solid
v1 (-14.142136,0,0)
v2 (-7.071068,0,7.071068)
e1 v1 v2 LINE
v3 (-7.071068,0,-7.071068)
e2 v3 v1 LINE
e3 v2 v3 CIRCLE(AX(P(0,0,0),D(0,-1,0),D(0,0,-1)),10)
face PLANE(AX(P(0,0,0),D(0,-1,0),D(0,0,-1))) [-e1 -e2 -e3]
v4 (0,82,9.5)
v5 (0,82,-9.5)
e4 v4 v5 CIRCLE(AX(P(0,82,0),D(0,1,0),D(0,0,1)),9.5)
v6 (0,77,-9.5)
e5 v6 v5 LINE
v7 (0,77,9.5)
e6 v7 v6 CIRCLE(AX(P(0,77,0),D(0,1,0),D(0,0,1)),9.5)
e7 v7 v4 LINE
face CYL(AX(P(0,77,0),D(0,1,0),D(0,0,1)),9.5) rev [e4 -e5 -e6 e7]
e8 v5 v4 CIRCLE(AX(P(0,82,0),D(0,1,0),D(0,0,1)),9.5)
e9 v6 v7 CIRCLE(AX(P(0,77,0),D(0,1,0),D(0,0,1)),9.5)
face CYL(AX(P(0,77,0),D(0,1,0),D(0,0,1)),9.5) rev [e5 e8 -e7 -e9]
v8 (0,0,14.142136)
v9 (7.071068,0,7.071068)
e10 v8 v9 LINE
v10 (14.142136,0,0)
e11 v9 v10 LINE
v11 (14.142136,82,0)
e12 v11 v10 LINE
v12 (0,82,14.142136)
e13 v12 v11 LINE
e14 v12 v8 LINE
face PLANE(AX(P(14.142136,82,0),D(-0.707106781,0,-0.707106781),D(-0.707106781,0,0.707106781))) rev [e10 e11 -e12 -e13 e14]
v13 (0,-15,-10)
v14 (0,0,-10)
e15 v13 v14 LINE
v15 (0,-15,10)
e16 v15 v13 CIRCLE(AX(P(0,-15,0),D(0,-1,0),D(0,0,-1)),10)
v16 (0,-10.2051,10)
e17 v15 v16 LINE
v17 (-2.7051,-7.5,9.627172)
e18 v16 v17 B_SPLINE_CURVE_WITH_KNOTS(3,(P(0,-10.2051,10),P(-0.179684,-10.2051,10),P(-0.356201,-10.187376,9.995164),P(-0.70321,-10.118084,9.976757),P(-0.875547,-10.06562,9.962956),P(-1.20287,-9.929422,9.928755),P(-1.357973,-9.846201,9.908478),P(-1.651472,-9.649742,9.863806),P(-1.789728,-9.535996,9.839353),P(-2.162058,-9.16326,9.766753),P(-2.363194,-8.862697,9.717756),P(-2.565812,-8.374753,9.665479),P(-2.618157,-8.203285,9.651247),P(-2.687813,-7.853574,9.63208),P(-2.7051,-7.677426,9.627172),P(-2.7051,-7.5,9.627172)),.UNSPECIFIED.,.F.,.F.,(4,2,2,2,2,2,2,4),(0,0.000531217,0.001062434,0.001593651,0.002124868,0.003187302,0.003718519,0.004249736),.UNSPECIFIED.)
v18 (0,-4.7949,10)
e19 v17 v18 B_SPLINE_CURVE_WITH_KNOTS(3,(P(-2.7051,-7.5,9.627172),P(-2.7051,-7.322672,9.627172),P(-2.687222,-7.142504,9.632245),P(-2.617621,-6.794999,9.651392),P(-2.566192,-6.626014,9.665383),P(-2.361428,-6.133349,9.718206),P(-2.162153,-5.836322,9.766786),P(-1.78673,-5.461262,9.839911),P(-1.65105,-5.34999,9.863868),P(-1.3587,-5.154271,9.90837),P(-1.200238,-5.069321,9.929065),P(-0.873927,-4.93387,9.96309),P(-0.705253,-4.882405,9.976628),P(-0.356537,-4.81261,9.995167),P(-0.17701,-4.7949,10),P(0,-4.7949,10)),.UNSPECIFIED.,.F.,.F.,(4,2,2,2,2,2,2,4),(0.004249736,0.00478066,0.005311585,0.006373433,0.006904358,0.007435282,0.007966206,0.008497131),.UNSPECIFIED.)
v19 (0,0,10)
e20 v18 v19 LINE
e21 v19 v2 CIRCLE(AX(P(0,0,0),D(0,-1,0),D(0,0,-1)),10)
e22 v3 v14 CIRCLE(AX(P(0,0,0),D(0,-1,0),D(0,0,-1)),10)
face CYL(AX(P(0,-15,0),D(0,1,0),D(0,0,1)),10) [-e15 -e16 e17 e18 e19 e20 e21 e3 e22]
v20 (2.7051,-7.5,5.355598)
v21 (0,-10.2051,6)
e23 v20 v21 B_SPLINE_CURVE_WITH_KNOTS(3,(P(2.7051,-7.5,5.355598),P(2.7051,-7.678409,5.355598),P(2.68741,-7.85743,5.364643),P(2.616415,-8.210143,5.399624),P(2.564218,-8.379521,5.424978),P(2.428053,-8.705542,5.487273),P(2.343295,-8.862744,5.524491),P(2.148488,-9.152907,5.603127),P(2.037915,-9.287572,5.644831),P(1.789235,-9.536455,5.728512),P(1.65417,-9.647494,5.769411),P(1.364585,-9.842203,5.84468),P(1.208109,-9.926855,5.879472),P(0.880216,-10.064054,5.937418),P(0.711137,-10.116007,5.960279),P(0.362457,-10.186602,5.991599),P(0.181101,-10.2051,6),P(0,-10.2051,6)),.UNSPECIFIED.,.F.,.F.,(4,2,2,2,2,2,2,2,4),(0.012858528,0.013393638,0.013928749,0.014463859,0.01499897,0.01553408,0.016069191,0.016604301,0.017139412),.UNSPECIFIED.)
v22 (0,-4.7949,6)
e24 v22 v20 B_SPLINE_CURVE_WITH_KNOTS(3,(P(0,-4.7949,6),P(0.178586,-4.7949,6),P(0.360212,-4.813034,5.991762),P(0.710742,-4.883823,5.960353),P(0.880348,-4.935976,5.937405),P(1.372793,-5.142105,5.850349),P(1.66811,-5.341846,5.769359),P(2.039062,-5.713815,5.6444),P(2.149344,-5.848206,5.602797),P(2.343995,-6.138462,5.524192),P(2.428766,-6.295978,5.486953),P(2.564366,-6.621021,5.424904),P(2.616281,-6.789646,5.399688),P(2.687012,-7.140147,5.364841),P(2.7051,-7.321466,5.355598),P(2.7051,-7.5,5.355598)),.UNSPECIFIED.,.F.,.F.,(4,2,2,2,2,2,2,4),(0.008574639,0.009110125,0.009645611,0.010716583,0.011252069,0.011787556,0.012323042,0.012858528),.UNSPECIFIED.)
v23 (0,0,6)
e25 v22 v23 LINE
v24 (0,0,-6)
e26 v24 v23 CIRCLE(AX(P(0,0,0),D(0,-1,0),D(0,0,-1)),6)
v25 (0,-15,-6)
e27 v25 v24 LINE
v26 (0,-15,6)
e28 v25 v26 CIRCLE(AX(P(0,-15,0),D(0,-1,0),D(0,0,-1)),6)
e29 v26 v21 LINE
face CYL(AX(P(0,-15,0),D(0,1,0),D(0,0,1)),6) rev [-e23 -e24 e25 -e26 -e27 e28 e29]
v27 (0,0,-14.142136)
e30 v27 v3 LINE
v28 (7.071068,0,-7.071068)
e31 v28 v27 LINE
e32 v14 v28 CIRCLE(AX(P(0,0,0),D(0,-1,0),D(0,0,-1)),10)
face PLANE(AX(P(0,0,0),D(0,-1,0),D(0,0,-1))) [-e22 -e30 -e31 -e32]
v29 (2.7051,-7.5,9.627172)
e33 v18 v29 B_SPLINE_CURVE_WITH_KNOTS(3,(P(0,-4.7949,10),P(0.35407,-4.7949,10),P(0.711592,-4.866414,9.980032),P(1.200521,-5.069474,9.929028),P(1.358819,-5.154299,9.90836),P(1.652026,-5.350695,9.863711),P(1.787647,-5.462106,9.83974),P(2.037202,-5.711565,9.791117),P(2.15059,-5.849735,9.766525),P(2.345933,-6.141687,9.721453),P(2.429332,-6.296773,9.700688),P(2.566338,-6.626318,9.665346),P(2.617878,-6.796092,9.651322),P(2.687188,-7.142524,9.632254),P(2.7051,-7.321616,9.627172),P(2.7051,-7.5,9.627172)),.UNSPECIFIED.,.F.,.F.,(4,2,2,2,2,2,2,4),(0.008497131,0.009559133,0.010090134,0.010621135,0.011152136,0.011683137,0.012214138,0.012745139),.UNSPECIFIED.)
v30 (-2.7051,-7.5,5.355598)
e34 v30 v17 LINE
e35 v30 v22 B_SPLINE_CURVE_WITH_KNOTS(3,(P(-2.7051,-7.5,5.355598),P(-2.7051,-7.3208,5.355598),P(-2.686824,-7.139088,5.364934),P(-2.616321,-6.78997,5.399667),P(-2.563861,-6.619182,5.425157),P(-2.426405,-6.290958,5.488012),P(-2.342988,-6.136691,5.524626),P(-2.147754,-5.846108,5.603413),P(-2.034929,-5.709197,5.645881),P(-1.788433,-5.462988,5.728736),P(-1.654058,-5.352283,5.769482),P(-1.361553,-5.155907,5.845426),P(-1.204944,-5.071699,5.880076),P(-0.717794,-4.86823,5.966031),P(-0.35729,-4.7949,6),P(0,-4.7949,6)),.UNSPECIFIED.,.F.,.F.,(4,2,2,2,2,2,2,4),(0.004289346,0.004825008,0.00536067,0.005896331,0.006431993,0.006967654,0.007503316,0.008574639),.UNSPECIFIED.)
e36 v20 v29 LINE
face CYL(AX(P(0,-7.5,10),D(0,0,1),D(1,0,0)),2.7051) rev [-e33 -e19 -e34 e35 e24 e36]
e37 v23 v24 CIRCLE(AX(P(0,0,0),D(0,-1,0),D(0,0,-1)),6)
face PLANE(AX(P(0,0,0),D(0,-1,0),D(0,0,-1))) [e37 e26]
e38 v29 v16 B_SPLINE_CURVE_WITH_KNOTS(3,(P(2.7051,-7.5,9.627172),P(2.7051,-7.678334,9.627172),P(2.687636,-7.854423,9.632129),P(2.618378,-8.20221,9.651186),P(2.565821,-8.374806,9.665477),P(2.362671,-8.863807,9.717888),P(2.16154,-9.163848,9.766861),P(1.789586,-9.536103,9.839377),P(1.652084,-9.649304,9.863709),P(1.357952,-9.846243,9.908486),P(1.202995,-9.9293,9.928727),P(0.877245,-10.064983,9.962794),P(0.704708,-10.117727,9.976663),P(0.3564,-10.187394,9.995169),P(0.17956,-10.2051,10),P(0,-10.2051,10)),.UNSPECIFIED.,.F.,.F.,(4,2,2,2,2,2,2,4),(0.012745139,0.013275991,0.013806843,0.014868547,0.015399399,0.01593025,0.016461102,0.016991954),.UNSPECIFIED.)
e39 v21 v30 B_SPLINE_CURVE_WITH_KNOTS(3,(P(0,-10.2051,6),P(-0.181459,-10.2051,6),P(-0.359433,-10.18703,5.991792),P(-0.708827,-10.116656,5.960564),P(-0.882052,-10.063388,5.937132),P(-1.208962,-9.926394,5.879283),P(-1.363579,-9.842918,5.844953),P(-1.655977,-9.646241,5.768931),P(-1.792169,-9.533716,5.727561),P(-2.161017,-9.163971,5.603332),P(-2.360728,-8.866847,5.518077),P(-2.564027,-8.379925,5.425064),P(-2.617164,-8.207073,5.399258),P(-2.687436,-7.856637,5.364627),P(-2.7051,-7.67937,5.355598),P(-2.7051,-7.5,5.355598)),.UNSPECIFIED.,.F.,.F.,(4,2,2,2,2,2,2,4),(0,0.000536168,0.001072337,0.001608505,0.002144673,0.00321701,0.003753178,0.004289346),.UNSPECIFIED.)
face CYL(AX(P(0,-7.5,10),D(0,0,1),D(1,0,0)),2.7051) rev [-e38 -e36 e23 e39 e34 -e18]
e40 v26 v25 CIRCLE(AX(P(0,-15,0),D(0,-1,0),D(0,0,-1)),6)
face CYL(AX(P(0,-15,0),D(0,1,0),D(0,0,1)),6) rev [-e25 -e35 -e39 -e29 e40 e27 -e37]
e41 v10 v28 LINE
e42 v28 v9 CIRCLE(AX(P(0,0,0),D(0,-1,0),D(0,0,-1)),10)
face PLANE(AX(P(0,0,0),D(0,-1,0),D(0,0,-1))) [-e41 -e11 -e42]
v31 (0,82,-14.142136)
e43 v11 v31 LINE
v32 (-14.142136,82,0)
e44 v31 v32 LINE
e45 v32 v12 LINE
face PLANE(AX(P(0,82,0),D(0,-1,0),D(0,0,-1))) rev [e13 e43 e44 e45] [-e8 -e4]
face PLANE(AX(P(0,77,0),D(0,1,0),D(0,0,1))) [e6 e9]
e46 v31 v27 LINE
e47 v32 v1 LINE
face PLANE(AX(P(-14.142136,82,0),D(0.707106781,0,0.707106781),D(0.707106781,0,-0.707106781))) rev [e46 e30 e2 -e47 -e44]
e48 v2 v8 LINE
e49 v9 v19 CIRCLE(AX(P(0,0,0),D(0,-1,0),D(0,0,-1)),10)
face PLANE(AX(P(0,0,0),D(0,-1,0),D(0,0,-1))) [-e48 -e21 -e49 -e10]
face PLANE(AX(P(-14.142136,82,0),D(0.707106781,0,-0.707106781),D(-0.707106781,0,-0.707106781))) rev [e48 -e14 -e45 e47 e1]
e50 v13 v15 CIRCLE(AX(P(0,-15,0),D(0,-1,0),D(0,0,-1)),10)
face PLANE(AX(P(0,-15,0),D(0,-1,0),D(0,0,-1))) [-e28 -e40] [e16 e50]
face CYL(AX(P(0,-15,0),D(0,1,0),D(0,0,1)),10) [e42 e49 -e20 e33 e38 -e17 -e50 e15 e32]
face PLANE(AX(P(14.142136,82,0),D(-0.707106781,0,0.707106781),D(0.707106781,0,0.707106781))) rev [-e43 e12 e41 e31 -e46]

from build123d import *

# Parameters (mm, degrees)
SQUARE_BAR_20X82_DEPTH          = 82
TOP_POCKET_PROFILE_19_R         = 9.5
TOP_POCKET_19X5_DEPTH           = 5
END_SPIGOT_PROFILE_20_R         = 10
END_SPIGOT_20X15_DEPTH          = 15
SKETCH3_3_R                     = 6
SPIGOT_CONTOUR_TRIM_CUT_DEPTH   = 85.403791384
CROSS_TAPPED_HOLE_1_4_28_REACH  = 95.771
CROSS_TAPPED_HOLE_1_4_28_BORE_R = 2.7051


with BuildPart() as part:
    # Square Bar Profile 20 → Square Bar 20x82 (new body)
    with BuildSketch(Plane(origin=(0, 0, 0), x_dir=(1, 0, 0), z_dir=(0, 1, 0))):
        Polygon((-14.142135624, 0), (0, 14.142135624), (14.142135624, 0), (0, -14.142135624), align=None)
    extrude(amount=SQUARE_BAR_20X82_DEPTH)

    # Top Pocket Profile _19 → Top Pocket _19x5 (cut)
    with BuildSketch(Plane(origin=(0, 82, 0), x_dir=(1, 0, 0), z_dir=(0, 1, 0))):
        with Locations(Location((0, 0, 0), (0, 0, 270))):
            Circle(TOP_POCKET_PROFILE_19_R)
    extrude(amount=-TOP_POCKET_19X5_DEPTH, mode=Mode.SUBTRACT)

    # End Spigot Profile _20 → End Spigot _20x15 (add)
    with BuildSketch(Plane.XZ):
        with Locations(Location((0, 0, 0), (0, 0, 45))):
            Circle(END_SPIGOT_PROFILE_20_R)
    extrude(amount=END_SPIGOT_20X15_DEPTH)

    # Sketch3_3 → Spigot Contour Trim Cut (cut, through all)
    with BuildSketch(Plane.XZ):
        with Locations(Location((0, 0, 0), (0, 0, 270))):
            Circle(SKETCH3_3_R)
    extrude(amount=SPIGOT_CONTOUR_TRIM_CUT_DEPTH, mode=Mode.SUBTRACT)

    # Cross Tapped Hole 1-4-28 bore (on position points) → Cross Tapped Hole 1-4-28 (cut, up to next)
    with BuildSketch(Plane(origin=(0, -7.5, 10), x_dir=(1, 0, 0), z_dir=(0, 0, 1)), mode=Mode.PRIVATE) as cross_tapped_hole_1_4_28_sk1:
        Circle(CROSS_TAPPED_HOLE_1_4_28_BORE_R)
    cross_tapped_hole_1_4_28_tool1 = extrude(cross_tapped_hole_1_4_28_sk1.sketch, amount=-CROSS_TAPPED_HOLE_1_4_28_REACH, mode=Mode.PRIVATE) & part.part
    add(cross_tapped_hole_1_4_28_tool1.solids().sort_by_distance((0, -7.5, 10))[0], mode=Mode.SUBTRACT)


solid = part.part
